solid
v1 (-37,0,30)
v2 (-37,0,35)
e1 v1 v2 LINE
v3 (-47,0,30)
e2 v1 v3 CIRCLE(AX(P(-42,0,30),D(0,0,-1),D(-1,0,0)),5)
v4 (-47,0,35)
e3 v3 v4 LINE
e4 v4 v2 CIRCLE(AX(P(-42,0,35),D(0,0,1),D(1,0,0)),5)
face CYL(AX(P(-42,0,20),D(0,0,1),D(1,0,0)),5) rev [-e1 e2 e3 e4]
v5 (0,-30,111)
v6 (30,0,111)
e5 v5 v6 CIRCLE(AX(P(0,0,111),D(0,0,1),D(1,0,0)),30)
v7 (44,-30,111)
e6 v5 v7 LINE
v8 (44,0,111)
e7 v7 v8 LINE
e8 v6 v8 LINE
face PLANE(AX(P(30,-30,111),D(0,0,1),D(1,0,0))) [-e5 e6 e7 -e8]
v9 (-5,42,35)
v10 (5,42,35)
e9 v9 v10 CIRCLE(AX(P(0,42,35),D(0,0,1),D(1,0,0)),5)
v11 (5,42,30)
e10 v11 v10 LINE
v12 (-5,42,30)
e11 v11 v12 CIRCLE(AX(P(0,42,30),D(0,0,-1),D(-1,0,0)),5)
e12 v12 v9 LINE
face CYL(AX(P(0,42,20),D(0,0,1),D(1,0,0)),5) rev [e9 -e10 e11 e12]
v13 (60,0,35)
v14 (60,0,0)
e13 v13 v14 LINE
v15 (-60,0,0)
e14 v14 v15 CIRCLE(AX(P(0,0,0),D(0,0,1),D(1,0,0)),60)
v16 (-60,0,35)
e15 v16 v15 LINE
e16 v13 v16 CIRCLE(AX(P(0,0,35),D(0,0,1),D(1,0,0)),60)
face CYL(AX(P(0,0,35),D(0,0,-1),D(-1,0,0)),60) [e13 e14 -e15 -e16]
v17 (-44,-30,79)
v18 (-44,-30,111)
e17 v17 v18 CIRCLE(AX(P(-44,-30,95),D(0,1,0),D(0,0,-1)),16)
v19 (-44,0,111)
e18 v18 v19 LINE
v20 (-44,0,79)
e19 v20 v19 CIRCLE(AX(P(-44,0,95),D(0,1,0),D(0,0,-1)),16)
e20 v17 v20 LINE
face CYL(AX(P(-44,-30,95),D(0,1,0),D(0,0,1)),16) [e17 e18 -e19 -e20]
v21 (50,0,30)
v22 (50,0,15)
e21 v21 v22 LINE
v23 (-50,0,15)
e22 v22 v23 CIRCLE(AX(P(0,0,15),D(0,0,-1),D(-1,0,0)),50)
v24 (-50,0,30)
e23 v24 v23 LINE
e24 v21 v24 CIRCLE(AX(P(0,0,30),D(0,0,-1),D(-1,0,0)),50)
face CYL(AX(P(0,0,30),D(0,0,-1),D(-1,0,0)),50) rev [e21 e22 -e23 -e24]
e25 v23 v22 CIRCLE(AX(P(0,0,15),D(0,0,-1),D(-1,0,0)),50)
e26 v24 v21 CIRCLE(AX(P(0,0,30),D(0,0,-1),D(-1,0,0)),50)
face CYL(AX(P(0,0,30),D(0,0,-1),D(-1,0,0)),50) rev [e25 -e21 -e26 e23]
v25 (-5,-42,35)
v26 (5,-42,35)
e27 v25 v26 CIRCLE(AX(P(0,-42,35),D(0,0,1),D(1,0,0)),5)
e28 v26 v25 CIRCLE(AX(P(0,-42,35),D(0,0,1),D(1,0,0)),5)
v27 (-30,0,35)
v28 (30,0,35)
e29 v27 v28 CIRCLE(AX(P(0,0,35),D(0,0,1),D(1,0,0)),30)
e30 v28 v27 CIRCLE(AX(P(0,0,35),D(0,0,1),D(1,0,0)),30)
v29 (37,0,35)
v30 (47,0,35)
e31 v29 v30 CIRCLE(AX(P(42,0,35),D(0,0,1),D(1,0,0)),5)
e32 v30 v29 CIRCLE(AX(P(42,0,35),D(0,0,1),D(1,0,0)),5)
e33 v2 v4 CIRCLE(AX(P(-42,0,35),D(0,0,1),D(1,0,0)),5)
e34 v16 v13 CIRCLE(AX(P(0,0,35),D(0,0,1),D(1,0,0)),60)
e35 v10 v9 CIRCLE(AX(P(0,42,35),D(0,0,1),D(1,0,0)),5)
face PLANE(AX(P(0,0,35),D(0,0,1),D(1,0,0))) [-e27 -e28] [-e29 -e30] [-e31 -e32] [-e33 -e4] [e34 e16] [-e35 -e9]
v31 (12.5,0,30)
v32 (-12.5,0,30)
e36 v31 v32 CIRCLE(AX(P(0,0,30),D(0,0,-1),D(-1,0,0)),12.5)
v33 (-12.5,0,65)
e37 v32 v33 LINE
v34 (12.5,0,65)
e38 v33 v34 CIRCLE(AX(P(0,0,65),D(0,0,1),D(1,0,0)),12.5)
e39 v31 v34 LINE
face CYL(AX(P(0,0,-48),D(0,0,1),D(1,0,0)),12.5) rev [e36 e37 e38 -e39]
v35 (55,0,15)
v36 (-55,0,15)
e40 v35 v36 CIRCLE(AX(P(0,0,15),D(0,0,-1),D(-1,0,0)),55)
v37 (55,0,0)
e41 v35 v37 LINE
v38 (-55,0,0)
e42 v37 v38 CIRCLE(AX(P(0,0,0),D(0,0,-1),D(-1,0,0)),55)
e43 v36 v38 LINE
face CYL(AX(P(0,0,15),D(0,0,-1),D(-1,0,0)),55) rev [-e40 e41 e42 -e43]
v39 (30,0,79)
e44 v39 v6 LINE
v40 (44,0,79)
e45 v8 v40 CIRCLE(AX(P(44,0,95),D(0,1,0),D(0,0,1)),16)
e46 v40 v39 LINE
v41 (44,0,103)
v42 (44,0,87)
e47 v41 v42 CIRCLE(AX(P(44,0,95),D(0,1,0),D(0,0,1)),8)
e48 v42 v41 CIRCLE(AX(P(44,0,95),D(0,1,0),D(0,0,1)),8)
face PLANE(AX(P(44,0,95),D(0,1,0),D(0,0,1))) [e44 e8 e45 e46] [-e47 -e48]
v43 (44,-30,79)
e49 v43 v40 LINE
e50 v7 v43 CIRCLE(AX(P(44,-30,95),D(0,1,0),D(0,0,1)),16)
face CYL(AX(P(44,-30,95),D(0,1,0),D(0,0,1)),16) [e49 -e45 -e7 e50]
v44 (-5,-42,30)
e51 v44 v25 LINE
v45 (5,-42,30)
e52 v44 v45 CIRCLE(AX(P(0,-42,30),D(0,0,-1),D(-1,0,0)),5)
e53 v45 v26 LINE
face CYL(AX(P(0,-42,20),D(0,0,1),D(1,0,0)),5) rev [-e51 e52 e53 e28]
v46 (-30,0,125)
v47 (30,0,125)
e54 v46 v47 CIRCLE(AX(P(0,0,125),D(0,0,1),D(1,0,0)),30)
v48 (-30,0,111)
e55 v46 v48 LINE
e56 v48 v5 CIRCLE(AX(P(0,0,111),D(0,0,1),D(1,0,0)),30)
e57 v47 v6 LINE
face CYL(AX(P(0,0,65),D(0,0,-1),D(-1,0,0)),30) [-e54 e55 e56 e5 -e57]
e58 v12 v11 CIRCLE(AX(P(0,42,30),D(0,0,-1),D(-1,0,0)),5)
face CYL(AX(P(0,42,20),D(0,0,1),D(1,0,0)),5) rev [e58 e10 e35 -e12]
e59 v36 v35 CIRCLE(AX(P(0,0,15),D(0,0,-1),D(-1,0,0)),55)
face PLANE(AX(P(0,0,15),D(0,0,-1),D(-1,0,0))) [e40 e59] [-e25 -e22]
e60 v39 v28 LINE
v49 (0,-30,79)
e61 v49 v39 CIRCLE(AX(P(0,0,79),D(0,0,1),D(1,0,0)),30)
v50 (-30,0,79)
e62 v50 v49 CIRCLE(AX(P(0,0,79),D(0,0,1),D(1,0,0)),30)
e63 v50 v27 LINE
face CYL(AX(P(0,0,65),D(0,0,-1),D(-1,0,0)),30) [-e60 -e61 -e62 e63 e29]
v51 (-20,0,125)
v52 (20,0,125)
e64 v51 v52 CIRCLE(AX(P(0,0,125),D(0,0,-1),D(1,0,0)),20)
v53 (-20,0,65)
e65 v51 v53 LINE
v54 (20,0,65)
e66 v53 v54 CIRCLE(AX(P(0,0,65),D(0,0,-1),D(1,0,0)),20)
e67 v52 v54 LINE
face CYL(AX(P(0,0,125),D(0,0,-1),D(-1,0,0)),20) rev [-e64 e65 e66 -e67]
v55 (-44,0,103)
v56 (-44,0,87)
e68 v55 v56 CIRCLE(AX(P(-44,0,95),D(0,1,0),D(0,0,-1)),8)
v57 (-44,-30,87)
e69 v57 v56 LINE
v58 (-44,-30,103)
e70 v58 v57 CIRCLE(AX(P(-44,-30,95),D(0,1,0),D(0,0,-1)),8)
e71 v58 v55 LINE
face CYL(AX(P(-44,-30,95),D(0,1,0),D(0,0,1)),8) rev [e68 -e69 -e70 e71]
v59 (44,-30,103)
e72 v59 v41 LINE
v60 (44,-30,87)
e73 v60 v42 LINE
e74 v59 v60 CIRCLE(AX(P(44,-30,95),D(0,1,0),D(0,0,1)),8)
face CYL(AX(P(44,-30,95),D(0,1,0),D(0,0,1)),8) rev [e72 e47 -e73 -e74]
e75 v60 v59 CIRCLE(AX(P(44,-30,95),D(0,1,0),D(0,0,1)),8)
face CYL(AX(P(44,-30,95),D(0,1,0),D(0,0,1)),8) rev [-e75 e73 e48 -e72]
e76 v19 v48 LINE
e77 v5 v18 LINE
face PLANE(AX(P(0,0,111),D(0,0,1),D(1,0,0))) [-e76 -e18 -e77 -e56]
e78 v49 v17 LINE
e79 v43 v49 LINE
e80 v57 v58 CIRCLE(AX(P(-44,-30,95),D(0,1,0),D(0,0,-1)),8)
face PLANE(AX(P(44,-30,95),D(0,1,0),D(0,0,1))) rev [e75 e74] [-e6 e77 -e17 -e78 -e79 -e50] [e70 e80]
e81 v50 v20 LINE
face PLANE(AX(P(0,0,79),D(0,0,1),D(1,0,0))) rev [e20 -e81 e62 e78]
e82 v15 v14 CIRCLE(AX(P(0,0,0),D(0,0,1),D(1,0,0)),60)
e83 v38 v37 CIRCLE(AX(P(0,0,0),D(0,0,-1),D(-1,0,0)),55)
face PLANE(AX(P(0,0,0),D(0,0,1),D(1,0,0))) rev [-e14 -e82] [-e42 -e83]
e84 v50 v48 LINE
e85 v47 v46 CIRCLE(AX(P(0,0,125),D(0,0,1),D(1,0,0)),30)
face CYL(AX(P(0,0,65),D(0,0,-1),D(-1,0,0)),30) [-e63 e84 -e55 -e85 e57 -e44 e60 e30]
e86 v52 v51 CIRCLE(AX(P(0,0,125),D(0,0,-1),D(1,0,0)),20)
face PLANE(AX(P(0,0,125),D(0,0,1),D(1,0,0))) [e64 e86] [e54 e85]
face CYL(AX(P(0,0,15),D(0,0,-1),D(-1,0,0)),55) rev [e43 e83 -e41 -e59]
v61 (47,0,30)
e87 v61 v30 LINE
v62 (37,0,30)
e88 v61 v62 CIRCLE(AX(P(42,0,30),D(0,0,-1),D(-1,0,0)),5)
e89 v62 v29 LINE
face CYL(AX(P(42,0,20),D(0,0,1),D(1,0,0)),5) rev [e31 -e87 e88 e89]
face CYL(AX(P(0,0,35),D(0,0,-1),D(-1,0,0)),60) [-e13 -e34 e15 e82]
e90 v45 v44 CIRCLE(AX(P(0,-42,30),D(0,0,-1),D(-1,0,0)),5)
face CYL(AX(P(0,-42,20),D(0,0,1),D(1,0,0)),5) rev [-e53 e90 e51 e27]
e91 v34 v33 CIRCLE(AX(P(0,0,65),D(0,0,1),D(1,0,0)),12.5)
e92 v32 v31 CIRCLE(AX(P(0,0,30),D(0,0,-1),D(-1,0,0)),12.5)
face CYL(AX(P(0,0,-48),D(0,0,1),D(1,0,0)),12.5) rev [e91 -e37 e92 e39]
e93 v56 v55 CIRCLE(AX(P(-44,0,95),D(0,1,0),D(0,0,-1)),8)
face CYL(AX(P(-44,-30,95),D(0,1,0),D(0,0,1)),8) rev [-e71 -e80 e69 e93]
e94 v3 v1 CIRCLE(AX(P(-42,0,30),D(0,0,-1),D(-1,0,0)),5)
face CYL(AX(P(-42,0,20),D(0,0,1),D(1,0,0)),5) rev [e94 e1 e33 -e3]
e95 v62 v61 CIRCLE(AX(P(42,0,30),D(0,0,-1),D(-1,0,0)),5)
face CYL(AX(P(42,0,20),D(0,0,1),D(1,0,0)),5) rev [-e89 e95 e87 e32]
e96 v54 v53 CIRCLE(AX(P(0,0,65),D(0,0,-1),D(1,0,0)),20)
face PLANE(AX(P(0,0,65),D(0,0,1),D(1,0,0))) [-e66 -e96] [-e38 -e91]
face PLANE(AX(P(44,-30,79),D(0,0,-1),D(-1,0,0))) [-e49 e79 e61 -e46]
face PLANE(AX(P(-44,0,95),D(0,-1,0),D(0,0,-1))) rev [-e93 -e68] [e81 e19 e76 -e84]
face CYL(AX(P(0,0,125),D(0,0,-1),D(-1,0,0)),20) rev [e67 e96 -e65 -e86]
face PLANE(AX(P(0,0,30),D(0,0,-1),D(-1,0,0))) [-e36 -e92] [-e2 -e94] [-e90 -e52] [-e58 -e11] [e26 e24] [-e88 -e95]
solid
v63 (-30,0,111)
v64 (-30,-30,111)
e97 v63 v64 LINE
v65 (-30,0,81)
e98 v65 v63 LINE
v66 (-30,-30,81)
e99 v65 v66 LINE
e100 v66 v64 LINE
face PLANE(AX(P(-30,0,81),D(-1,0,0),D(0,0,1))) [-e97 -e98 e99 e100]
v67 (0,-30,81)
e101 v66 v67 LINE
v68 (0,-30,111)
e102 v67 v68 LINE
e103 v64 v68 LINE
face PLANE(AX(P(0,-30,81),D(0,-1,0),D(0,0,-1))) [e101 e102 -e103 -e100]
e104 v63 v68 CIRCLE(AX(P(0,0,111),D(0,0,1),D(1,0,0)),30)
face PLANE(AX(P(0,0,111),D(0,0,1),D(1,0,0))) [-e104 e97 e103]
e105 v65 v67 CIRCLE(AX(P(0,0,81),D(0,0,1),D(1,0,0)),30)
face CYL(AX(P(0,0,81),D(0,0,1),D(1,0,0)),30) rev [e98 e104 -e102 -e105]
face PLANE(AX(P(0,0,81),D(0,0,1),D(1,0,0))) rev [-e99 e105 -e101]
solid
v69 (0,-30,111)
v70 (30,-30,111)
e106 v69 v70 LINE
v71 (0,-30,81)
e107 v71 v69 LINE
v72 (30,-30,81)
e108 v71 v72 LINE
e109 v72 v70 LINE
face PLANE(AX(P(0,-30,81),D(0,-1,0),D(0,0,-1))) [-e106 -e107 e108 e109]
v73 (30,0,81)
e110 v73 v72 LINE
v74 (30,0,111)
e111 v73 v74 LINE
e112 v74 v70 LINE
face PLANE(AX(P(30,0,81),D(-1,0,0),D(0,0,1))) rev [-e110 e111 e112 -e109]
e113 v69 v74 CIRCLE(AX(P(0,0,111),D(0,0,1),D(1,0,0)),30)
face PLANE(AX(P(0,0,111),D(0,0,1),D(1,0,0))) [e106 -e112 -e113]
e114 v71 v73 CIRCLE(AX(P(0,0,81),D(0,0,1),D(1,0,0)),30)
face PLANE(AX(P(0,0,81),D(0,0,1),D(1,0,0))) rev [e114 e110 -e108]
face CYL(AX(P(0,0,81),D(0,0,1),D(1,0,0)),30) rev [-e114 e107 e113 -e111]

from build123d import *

# Parameters (mm, degrees)
FLANGE_SKETCH_120_R        = 60
FLANGE_120_DEPTH           = 35
FLANGE_RECESS_SKETCH_110_R = 55
FLANGE_RECESS_110_DEPTH    = 15
FLANGE_INNER_CUT_SKETCH_R  = 50
FLANGE_INNER_CUT_DEPTH     = 15
BOLT_HOLES_SKETCH_4X_10_R  = 5
BOLT_HOLES_4X_10_DEPTH     = 15
HUB_SKETCH_60_R            = 30
HUB_60_DEPTH               = 30
HUB_EXTENSION_DEPTH        = 60
CLAMP_LUGS_SKETCH_R        = 8
CLAMP_LUGS_DEPTH           = 30
CLAMP_LUGS_2_DEPTH         = 30
SHAFT_BORE_SKETCH_R        = 12.5
SHAFT_BORE_DEPTH           = 113
HUB_START                  = -60
HUB_TUBE_SKETCH_60_40_R    = 30
HUB_TUBE_SKETCH_60_40_R_2  = 20
HUB_TUBE_DEPTH             = 60
LUG_START                  = -32
LUG_WEB_B_DEPTH            = 32
LUG_WEB_A_DEPTH            = 30
LUG_WEB_A_2_DEPTH          = 30


with BuildPart() as part:
    # Flange Sketch Ø120 → Flange Ø120 (new body)
    with BuildSketch(Plane.XY):
        Circle(FLANGE_SKETCH_120_R)
    extrude(amount=FLANGE_120_DEPTH)

    # Flange Recess Sketch Ø110 → Flange Recess Ø110 (cut)
    with BuildSketch(Plane(origin=(0, 0, 0), x_dir=(-1, 0, 0), z_dir=(0, 0, -1))):
        Circle(FLANGE_RECESS_SKETCH_110_R)
    extrude(amount=-FLANGE_RECESS_110_DEPTH, mode=Mode.SUBTRACT)

    # Flange Inner Cut Sketch → Flange Inner Cut (cut)
    with BuildSketch(Plane(origin=(0, 0, 15), x_dir=(-1, 0, 0), z_dir=(0, 0, -1))):
        Circle(FLANGE_INNER_CUT_SKETCH_R)
    extrude(amount=-FLANGE_INNER_CUT_DEPTH, mode=Mode.SUBTRACT)

    # Bolt Holes Sketch 4xØ10 → Bolt Holes 4xØ10 (cut)
    with BuildSketch(Plane.XY.offset(35)):
        with Locations((42, 0)):
            Circle(BOLT_HOLES_SKETCH_4X_10_R)
        with Locations((0, -42)):
            Circle(BOLT_HOLES_SKETCH_4X_10_R)
        with Locations((-42, 0)):
            Circle(BOLT_HOLES_SKETCH_4X_10_R)
        with Locations((0, 42)):
            Circle(BOLT_HOLES_SKETCH_4X_10_R)
    extrude(amount=-BOLT_HOLES_4X_10_DEPTH, mode=Mode.SUBTRACT)

    # Hub Sketch Ø60 → Hub Ø60 (add)
    with BuildSketch(Plane.XY.offset(35)):
        Circle(HUB_SKETCH_60_R)
    extrude(amount=HUB_60_DEPTH)

    # Hub Extension Sketch → Hub Extension (add)
    with BuildSketch(Plane.XY.offset(65)):
        with BuildLine():
            Line((-30, 0), (-20, 0))
            ThreePointArc((-20, 0), (0, -20), (20, 0))
            Line((20, 0), (30, 0))
            ThreePointArc((30, 0), (0, -30), (-30, 0))
        make_face()
    extrude(amount=HUB_EXTENSION_DEPTH)

    # Shaft Bore Sketch → Shaft Bore (cut)
    with BuildSketch(Plane.XY.offset(65)):
        Circle(SHAFT_BORE_SKETCH_R)
    extrude(amount=-SHAFT_BORE_DEPTH, mode=Mode.SUBTRACT)

    # Hub Tube Sketch Ø60-Ø40 → Hub Tube (add)
    with BuildSketch(Plane.XY.offset(125).offset(HUB_START)):
        Circle(HUB_TUBE_SKETCH_60_40_R)
        with Locations(Location((0, 0, 0), (0, 0, 180))):
            Circle(HUB_TUBE_SKETCH_60_40_R_2, mode=Mode.SUBTRACT)
    extrude(amount=HUB_TUBE_DEPTH)



with BuildPart() as body_2:
    # Clamp Lugs Sketch → Clamp Lugs (new body)
    with BuildSketch(Plane(origin=(0, 0, 0), x_dir=(1, 0, 0), z_dir=(0, 1, 0))):
        with BuildLine():
            Line((44, -79), (30, -79))
            Line((30, -79), (30, -111))
            Line((30, -111), (44, -111))
            ThreePointArc((44, -111), (60, -95), (44, -79))
        make_face()
        with Locations(Location((44, -95, 0), (0, 0, 270))):
            Circle(CLAMP_LUGS_SKETCH_R, mode=Mode.SUBTRACT)
    extrude(amount=-CLAMP_LUGS_DEPTH)


with BuildPart() as body_3:
    # Clamp Lugs Sketch → Clamp Lugs 2 (new body)
    with BuildSketch(Plane(origin=(0, 0, 0), x_dir=(1, 0, 0), z_dir=(0, 1, 0))):
        with BuildLine():
            Line((-30, -111), (-44, -111))
            ThreePointArc((-44, -111), (-60, -95), (-44, -79))
            Line((-44, -79), (-30, -79))
            Line((-30, -79), (-30, -111))
        make_face()
        with Locations(Location((-44, -95, 0), (0, 0, 90))):
            Circle(CLAMP_LUGS_SKETCH_R, mode=Mode.SUBTRACT)
    extrude(amount=-CLAMP_LUGS_2_DEPTH)


with BuildPart() as part_1:
    add(part.part)

    add(body_2.part)  # Lug Web B merges body 2

    add(body_3.part)  # Lug Web B merges body 3
    # Lug Web B Sketch → Lug Web B (add)
    with BuildSketch(Plane.XY.offset(111).offset(LUG_START)):
        with BuildLine():
            Line((30, -30), (30, 0))
            ThreePointArc((30, 0), (21.213203436, -21.213203436), (0, -30))
            Line((0, -30), (30, -30))
        make_face()
        with BuildLine():
            Line((-30, -30), (0, -30))
            ThreePointArc((0, -30), (-21.213203436, -21.213203436), (-30, 0))
            Line((-30, 0), (-30, -30))
        make_face()
    extrude(amount=LUG_WEB_B_DEPTH)


with BuildPart() as body_2_2:
    # Lug Web A Sketch → Lug Web A (new body)
    with BuildSketch(Plane.XY.offset(111)):
        with BuildLine():
            Line((0, -30), (30, -30))
            Line((30, -30), (30, 0))
            ThreePointArc((30, 0), (21.213203436, -21.213203436), (0, -30))
        make_face()
    extrude(amount=-LUG_WEB_A_DEPTH)


with BuildPart() as body_3_2:
    # Lug Web A Sketch → Lug Web A 2 (new body)
    with BuildSketch(Plane.XY.offset(111)):
        with BuildLine():
            Line((-30, -30), (0, -30))
            ThreePointArc((0, -30), (-21.213203436, -21.213203436), (-30, 0))
            Line((-30, 0), (-30, -30))
        make_face()
    extrude(amount=-LUG_WEB_A_2_DEPTH)


solid = Compound([part_1.part, body_2_2.part, body_3_2.part])
